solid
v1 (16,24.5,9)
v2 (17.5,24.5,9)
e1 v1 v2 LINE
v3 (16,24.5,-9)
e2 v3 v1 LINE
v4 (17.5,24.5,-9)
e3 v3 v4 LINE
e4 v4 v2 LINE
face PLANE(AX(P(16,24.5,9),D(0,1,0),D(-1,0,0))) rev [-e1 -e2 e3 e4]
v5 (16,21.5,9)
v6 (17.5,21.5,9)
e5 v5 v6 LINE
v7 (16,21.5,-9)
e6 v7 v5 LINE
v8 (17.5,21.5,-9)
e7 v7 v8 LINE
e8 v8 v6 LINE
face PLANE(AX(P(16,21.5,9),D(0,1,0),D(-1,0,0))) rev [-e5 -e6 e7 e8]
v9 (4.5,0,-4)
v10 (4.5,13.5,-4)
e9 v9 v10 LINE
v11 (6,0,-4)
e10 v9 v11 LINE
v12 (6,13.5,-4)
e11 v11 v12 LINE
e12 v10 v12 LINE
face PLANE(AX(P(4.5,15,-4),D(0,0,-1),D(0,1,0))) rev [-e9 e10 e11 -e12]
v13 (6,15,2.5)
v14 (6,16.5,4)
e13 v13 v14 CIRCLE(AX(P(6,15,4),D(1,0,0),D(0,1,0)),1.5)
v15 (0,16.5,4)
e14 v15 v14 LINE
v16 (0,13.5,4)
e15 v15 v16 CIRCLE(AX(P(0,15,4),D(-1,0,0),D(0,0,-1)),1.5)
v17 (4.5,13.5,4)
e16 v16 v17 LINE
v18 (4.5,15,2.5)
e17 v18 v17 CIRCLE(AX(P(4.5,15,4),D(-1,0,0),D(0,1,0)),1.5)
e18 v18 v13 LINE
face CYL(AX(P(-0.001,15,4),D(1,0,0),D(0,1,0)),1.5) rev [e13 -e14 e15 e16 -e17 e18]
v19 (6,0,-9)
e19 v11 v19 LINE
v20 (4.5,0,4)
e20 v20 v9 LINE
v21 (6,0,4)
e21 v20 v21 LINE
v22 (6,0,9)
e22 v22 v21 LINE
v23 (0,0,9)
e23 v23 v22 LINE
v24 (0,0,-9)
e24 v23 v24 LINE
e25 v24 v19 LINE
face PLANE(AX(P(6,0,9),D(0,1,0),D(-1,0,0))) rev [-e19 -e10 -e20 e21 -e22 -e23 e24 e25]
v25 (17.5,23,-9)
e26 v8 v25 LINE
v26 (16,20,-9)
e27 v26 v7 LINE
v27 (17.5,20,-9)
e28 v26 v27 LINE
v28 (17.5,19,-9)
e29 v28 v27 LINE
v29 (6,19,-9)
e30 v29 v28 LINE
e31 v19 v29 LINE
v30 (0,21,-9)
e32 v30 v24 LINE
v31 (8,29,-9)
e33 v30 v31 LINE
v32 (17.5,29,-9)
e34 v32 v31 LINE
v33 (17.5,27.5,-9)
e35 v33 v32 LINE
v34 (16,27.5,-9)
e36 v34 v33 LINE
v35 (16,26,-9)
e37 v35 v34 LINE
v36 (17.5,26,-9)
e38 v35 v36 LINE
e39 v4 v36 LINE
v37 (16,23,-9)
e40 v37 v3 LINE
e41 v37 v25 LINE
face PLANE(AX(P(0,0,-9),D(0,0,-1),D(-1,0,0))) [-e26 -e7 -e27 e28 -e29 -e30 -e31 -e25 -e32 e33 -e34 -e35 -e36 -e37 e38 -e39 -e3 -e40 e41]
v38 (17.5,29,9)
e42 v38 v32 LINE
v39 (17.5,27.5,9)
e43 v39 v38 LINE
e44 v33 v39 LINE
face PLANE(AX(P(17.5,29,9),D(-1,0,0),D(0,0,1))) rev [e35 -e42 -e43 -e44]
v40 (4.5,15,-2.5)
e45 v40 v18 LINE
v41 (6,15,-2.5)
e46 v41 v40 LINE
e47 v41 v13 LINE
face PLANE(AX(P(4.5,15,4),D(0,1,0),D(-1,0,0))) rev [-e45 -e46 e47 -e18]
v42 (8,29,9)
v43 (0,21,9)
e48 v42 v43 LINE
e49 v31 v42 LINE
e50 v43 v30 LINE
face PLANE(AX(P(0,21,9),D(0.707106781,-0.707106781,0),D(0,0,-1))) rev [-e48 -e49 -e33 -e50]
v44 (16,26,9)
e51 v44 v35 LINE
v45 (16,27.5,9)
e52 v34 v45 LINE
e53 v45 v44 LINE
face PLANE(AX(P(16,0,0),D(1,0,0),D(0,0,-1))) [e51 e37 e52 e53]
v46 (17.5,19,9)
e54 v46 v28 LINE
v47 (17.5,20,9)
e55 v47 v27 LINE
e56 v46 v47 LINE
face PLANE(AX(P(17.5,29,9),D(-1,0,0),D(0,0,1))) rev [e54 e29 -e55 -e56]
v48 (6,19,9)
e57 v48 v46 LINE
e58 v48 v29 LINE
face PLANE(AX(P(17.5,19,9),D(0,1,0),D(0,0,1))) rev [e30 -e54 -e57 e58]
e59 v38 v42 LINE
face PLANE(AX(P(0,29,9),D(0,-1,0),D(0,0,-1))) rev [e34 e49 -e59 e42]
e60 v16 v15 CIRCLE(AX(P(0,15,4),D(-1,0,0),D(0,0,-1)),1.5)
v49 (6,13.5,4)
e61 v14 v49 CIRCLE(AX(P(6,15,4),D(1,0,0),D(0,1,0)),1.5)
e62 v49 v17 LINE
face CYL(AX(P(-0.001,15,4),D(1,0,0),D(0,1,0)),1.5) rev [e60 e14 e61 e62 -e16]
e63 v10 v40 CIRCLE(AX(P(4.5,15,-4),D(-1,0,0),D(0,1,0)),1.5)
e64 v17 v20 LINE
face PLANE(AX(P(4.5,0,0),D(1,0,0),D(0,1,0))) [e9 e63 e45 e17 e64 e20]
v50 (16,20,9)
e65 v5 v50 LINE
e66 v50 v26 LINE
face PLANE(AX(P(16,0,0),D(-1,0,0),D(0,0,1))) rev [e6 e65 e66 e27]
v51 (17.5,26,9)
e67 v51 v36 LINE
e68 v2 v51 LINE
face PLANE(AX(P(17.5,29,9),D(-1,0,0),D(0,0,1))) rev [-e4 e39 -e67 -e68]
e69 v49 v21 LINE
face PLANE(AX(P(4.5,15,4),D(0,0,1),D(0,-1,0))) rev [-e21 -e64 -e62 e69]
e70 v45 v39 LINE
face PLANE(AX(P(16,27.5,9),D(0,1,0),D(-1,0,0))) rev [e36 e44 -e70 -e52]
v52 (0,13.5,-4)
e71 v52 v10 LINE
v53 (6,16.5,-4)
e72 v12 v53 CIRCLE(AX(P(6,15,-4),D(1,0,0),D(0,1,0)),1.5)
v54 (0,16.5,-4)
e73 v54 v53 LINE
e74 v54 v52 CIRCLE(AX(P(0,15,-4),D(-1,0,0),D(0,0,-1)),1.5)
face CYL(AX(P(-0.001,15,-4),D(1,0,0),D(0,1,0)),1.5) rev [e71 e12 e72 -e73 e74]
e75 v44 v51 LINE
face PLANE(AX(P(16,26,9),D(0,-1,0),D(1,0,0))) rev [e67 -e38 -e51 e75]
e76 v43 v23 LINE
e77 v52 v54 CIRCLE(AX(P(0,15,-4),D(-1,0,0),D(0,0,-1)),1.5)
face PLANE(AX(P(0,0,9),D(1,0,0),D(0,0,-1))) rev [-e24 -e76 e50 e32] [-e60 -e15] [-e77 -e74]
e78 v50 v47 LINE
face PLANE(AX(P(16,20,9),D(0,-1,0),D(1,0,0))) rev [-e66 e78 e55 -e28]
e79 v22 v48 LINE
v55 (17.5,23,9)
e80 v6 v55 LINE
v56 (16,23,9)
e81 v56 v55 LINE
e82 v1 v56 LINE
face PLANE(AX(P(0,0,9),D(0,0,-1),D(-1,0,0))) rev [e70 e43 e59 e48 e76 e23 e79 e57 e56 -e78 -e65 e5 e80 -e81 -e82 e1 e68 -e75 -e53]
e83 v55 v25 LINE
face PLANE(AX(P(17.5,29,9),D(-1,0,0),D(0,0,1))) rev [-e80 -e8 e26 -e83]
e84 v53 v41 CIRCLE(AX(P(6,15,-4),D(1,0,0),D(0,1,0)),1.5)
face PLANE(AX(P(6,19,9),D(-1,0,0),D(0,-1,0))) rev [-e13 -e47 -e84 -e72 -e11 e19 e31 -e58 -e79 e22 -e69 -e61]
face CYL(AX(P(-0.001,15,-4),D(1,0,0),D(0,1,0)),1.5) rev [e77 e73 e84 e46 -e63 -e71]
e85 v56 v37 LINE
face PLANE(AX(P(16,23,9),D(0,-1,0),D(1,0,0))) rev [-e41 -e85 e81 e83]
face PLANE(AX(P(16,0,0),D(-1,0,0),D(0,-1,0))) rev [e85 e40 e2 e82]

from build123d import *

# Parameters (mm, degrees)
EXTRUDE_1_DEPTH     = 9
SKETCH_2_W          = 8
SKETCH_2_H          = 15
CUT_EXTRUDE_1_DEPTH = 1.5
CUT_EXTRUDE_2_REACH = 34.469
SKETCH_3_R          = 1.5
SKETCH_4_W          = 18
SKETCH_4_H          = 1.5
CUT_EXTRUDE_3_DEPTH = 1.5
CHAMFER_1_SIZE      = 8


with BuildPart() as part:
    # 草图1 → 凸台-拉伸1 (new, symmetric)
    with BuildSketch(Plane.XY):
        Polygon((0, 0), (0, 29), (17.5, 29), (17.5, 19), (6, 19), (6, 0), align=None)
    extrude(amount=EXTRUDE_1_DEPTH, both=True)

    # 草图2 → 切除-拉伸1 (cut)
    with BuildSketch(Plane(origin=(6, 0, 0), x_dir=(0, 0, -1), z_dir=(1, 0, 0))):
        with Locations((0, 7.5)):
            Rectangle(SKETCH_2_W, SKETCH_2_H)
    extrude(amount=-CUT_EXTRUDE_1_DEPTH, mode=Mode.SUBTRACT)

    # 草图3 → 切除-拉伸2 (cut, up to next)
    with BuildSketch(Plane(origin=(6, 0, 0), x_dir=(0, 0, -1), z_dir=(1, 0, 0)), mode=Mode.PRIVATE) as cut_extrude_2_sk1:
        with Locations(Location((4, 15, 0), (0, 0, 180))):
            Circle(SKETCH_3_R)
    cut_extrude_2_tool1 = extrude(cut_extrude_2_sk1.sketch, amount=-CUT_EXTRUDE_2_REACH, mode=Mode.PRIVATE) & part.part
    # 草图3 → 切除-拉伸2 (cut, up to next)
    with BuildSketch(Plane(origin=(6, 0, 0), x_dir=(0, 0, -1), z_dir=(1, 0, 0)), mode=Mode.PRIVATE) as cut_extrude_2_sk2:
        with Locations((-4, 15)):
            Circle(SKETCH_3_R)
    cut_extrude_2_tool2 = extrude(cut_extrude_2_sk2.sketch, amount=-CUT_EXTRUDE_2_REACH, mode=Mode.PRIVATE) & part.part
    add(cut_extrude_2_tool1.solids().sort_by_distance((6, 15, -4))[0], mode=Mode.SUBTRACT)
    add(cut_extrude_2_tool2.solids().sort_by_distance((6, 15, 4))[0], mode=Mode.SUBTRACT)

    # 草图4 → 切除-拉伸3 (cut)
    with BuildSketch(Plane(origin=(17.5, 0, 0), x_dir=(0, 0, -1), z_dir=(1, 0, 0))):
        with Locations((0, 26.75)):
            Rectangle(SKETCH_4_W, SKETCH_4_H)
        with Locations((0, 23.75)):
            Rectangle(SKETCH_4_W, SKETCH_4_H)
        with Locations((0, 20.75)):
            Rectangle(SKETCH_4_W, SKETCH_4_H)
    extrude(amount=-CUT_EXTRUDE_3_DEPTH, mode=Mode.SUBTRACT)

    # 倒角1
    chamfer_1_edges = [part.edges().sort_by_distance(p)[0] for p in [
        (0, 29, 0),
    ]]
    chamfer(chamfer_1_edges, length=CHAMFER_1_SIZE)


solid = part.part
